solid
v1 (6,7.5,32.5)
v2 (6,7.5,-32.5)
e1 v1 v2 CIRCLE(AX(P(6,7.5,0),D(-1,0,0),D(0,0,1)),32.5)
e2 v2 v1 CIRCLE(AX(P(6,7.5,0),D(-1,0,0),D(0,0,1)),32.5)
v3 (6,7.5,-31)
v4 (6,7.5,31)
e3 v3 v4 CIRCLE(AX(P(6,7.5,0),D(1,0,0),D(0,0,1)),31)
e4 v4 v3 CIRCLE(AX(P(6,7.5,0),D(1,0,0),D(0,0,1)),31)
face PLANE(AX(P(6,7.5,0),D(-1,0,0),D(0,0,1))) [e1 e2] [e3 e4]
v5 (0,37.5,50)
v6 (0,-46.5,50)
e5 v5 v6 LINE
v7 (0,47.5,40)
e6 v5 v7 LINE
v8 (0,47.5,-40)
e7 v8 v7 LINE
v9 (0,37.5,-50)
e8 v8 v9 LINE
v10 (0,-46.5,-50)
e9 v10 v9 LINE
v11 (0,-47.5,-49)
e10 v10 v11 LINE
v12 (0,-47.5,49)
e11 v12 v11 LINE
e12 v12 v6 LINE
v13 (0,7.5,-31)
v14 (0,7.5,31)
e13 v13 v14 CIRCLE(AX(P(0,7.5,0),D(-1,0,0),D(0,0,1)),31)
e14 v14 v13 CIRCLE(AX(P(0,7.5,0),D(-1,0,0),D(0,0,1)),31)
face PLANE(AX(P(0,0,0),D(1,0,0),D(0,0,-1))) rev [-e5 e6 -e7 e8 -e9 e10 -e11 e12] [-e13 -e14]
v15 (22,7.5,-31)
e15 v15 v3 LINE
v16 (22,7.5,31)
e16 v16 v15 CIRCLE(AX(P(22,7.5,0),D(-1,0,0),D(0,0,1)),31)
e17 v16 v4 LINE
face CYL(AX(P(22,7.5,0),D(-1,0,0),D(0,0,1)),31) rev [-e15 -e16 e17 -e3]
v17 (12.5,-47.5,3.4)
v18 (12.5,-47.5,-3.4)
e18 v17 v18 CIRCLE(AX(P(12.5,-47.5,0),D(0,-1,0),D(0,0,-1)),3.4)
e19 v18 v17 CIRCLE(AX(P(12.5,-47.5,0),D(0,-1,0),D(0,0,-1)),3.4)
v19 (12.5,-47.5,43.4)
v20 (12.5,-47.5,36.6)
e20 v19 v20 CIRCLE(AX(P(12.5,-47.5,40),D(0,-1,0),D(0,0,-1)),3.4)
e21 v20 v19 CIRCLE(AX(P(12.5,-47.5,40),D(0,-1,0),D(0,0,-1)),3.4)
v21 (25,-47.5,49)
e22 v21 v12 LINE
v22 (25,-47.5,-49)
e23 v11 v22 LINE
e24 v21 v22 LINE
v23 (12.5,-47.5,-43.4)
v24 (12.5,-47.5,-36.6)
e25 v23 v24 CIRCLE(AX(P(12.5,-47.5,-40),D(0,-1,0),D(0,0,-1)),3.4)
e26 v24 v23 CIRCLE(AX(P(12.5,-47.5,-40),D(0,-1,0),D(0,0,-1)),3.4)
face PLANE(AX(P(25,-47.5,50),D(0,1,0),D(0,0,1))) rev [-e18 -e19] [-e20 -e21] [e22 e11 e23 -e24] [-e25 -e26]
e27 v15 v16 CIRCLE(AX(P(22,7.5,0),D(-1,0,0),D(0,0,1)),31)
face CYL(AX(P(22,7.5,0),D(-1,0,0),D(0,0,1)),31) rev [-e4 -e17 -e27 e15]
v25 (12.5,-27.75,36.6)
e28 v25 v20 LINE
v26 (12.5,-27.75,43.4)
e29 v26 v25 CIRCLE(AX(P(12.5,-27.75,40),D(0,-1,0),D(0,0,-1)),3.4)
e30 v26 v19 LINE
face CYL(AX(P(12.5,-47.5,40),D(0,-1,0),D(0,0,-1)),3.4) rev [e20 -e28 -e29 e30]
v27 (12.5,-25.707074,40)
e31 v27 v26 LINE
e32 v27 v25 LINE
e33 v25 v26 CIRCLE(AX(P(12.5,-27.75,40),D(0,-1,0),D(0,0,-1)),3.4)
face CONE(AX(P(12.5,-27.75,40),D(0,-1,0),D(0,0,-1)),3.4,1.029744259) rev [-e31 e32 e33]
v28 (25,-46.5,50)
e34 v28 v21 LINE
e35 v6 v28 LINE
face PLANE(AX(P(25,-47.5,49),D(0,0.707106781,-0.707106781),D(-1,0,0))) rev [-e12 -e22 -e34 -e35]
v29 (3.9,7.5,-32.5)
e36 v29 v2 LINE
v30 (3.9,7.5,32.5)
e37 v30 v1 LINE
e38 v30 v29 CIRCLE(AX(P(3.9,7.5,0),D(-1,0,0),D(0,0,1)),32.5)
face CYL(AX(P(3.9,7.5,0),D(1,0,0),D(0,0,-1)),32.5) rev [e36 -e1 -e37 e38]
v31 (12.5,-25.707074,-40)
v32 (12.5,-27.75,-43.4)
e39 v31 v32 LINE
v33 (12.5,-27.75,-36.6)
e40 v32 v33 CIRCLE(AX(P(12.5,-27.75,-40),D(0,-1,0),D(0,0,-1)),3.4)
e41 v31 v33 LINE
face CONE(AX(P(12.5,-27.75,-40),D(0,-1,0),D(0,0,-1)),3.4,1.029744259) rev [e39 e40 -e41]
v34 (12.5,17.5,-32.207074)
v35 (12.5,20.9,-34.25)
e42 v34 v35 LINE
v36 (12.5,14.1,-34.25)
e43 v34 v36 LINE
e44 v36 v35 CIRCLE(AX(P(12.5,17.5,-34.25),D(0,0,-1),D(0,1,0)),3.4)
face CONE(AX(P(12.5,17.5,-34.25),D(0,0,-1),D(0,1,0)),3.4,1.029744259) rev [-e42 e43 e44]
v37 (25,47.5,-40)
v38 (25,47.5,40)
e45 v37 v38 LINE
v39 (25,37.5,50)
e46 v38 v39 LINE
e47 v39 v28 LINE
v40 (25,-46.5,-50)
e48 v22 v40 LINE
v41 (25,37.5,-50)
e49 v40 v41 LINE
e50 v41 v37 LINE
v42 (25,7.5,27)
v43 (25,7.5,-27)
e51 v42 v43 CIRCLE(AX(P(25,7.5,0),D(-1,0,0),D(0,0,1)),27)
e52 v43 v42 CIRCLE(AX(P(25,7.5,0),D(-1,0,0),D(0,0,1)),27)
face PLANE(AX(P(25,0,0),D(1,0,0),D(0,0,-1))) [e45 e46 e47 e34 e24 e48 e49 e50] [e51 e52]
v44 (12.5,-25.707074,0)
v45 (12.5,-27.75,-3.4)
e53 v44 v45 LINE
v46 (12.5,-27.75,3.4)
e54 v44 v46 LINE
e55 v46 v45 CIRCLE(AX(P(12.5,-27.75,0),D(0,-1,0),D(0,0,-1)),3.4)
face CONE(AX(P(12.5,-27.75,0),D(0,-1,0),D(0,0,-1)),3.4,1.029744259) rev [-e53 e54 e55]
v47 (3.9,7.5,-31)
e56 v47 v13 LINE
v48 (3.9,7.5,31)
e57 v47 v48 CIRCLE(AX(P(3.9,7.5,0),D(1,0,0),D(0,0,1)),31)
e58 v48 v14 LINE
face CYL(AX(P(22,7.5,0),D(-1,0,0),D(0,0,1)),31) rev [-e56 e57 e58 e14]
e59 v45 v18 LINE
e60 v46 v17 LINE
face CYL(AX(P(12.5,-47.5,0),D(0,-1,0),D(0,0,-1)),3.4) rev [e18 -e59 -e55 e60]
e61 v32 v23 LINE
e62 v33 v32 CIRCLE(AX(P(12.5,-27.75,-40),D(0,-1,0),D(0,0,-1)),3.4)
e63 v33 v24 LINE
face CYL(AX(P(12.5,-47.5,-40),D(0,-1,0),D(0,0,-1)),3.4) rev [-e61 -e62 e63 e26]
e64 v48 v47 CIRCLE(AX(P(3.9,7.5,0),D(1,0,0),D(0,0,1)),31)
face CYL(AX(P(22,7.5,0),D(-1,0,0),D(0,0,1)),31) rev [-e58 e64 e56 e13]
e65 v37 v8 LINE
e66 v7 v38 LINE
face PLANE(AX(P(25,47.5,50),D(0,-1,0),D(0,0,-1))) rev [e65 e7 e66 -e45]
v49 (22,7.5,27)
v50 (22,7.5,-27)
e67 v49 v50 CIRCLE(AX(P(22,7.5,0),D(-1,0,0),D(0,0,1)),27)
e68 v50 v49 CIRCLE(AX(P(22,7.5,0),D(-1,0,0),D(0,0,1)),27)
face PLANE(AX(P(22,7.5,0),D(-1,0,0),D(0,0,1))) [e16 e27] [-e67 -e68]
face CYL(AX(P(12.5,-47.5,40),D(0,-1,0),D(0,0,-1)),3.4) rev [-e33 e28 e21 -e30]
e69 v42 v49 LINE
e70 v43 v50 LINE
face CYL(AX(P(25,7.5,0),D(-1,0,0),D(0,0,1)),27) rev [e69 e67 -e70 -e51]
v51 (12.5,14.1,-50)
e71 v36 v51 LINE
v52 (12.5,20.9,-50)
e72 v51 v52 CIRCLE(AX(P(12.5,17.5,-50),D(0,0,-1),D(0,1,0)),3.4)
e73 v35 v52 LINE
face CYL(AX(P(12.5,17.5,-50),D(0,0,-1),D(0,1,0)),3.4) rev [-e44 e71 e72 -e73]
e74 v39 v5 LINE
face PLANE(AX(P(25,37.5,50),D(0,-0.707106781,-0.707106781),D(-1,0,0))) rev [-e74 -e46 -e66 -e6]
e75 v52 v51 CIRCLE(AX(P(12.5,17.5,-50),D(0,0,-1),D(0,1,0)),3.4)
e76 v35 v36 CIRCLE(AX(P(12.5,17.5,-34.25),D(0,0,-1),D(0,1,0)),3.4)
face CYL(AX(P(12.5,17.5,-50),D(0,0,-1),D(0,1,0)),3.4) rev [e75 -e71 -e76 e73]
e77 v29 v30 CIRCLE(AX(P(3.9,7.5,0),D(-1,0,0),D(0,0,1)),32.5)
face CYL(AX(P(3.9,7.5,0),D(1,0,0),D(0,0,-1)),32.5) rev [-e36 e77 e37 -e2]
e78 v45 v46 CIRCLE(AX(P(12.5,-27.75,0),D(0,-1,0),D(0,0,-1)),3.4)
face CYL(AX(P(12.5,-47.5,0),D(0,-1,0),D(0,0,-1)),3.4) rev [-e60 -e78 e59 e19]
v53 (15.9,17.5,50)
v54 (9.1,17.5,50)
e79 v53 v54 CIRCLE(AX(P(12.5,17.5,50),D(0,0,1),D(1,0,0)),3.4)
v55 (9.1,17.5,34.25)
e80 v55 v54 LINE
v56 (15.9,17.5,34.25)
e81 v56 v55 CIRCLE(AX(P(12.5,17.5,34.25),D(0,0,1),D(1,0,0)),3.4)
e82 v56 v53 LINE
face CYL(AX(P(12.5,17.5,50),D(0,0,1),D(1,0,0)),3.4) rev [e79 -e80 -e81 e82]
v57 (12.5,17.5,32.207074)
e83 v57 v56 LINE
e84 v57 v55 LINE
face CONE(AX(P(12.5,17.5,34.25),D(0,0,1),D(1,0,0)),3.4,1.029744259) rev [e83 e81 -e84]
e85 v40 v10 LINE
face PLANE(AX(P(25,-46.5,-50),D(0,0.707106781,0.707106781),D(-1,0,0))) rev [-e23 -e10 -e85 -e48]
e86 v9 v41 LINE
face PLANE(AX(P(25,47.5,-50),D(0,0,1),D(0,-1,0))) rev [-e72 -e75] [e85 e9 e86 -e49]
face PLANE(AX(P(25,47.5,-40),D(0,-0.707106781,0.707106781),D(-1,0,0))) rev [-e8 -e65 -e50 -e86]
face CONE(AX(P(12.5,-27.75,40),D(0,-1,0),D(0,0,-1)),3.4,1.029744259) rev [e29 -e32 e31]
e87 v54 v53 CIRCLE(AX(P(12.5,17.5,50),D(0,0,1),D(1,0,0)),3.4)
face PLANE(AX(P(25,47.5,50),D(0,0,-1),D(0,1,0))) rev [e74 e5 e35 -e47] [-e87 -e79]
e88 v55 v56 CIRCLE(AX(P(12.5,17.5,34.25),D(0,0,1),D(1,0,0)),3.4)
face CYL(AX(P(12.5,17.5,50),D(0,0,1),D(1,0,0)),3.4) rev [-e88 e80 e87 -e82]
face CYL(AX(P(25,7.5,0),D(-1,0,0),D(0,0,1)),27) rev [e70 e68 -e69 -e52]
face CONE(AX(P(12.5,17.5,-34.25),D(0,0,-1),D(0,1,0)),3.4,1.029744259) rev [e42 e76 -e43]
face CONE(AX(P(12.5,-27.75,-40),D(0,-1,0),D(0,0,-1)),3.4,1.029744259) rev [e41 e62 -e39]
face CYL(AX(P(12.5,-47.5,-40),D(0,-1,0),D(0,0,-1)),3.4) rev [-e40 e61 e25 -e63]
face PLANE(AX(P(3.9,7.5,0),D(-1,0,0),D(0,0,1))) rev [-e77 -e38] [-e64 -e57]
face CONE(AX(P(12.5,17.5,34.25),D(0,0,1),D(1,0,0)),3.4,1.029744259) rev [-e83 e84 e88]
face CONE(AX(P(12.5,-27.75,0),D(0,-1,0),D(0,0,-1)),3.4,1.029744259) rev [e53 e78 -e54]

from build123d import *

# Parameters (mm, degrees)
SKETCH_1_W             = 100
SKETCH_1_H             = 95
EXTRUDE_1_DEPTH        = 25
SKETCH_2_R             = 31
CUT_EXTRUDE_1_DEPTH    = 22
SKETCH_3_R             = 27
CUT_EXTRUDE_2_DEPTH    = 73.389571072
CUT_EXTRUDE_START      = 16
SKETCH_4_R             = 32.5
CUT_EXTRUDE_3_DEPTH    = 2.1
HOLE_WIZARD_M8_1_D     = 6.8
HOLE_WIZARD_M8_1_DEPTH = 15.75
HOLE_WIZARD_M8_1_TIP   = 2.042926105
HOLE_WIZARD_M8_2_D     = 6.8
HOLE_WIZARD_M8_2_DEPTH = 15.75
HOLE_WIZARD_M8_2_TIP   = 2.042926105
CHAMFER_1_SIZE         = 10
CHAMFER_2_SIZE         = 1
HOLE_WIZARD_M8_3_D     = 6.8
HOLE_WIZARD_M8_3_DEPTH = 19.75
HOLE_WIZARD_M8_3_TIP   = 2.042926105


with BuildPart() as part:
    # 草图1 → 凸台-拉伸1 (new body)
    with BuildSketch(Plane(origin=(0, 0, 0), x_dir=(0, 0, -1), z_dir=(1, 0, 0))):
        Rectangle(SKETCH_1_W, SKETCH_1_H)
    extrude(amount=EXTRUDE_1_DEPTH)

    # 草图2 → 切除-拉伸1 (cut)
    with BuildSketch(Plane.ZY):
        with Locations((0, 7.5)):
            Circle(SKETCH_2_R)
    extrude(amount=-CUT_EXTRUDE_1_DEPTH, mode=Mode.SUBTRACT)

    # 草图3 → 切除-拉伸2 (cut, through all)
    with BuildSketch(Plane.ZY.offset(-22)):
        with Locations((0, 7.5)):
            Circle(SKETCH_3_R)
    extrude(amount=-CUT_EXTRUDE_2_DEPTH, mode=Mode.SUBTRACT)

    # 草图4 → 切除-拉伸3 (cut)
    with BuildSketch(Plane.ZY.offset(-22).offset(CUT_EXTRUDE_START)):
        with Locations((0, 7.5)):
            Circle(SKETCH_4_R)
    extrude(amount=CUT_EXTRUDE_3_DEPTH, mode=Mode.SUBTRACT)

    # M8 螺纹孔1
    with Locations(Plane.XY.offset(50)):
        with Locations((12.5, 17.5)):
            Hole(HOLE_WIZARD_M8_1_D / 2, depth=HOLE_WIZARD_M8_1_DEPTH)
            with Locations((0, 0, -(HOLE_WIZARD_M8_1_DEPTH + HOLE_WIZARD_M8_1_TIP / 2))):  # 118° drill point
                Cone(0, HOLE_WIZARD_M8_1_D / 2, HOLE_WIZARD_M8_1_TIP, mode=Mode.SUBTRACT)

    # M8 螺纹孔2
    with Locations(Plane(origin=(0, 0, -50), x_dir=(-1, 0, 0), z_dir=(0, 0, -1))):
        with Locations((-12.5, 17.5)):
            Hole(HOLE_WIZARD_M8_2_D / 2, depth=HOLE_WIZARD_M8_2_DEPTH)
            with Locations((0, 0, -(HOLE_WIZARD_M8_2_DEPTH + HOLE_WIZARD_M8_2_TIP / 2))):  # 118° drill point
                Cone(0, HOLE_WIZARD_M8_2_D / 2, HOLE_WIZARD_M8_2_TIP, mode=Mode.SUBTRACT)

    # 倒角1
    chamfer_1_edges = [part.edges().sort_by_distance(p)[0] for p in [
        (12.5, 47.5, 50),
        (12.5, 47.5, -50),
    ]]
    chamfer(chamfer_1_edges, length=CHAMFER_1_SIZE)

    # 倒角2
    chamfer_2_edges = [part.edges().sort_by_distance(p)[0] for p in [
        (12.5, -47.5, -50),
        (12.5, -47.5, 50),
    ]]
    chamfer(chamfer_2_edges, length=CHAMFER_2_SIZE)

    # M8 螺纹孔3
    with Locations(Plane(origin=(0, -47.5, 0), x_dir=(-1, 0, 0), z_dir=(0, -1, 0))):
        with Locations((-12.5, -40), (-12.5, 0), (-12.5, 40)):
            Hole(HOLE_WIZARD_M8_3_D / 2, depth=HOLE_WIZARD_M8_3_DEPTH)
            with Locations((0, 0, -(HOLE_WIZARD_M8_3_DEPTH + HOLE_WIZARD_M8_3_TIP / 2))):  # 118° drill point
                Cone(0, HOLE_WIZARD_M8_3_D / 2, HOLE_WIZARD_M8_3_TIP, mode=Mode.SUBTRACT)


solid = part.part
